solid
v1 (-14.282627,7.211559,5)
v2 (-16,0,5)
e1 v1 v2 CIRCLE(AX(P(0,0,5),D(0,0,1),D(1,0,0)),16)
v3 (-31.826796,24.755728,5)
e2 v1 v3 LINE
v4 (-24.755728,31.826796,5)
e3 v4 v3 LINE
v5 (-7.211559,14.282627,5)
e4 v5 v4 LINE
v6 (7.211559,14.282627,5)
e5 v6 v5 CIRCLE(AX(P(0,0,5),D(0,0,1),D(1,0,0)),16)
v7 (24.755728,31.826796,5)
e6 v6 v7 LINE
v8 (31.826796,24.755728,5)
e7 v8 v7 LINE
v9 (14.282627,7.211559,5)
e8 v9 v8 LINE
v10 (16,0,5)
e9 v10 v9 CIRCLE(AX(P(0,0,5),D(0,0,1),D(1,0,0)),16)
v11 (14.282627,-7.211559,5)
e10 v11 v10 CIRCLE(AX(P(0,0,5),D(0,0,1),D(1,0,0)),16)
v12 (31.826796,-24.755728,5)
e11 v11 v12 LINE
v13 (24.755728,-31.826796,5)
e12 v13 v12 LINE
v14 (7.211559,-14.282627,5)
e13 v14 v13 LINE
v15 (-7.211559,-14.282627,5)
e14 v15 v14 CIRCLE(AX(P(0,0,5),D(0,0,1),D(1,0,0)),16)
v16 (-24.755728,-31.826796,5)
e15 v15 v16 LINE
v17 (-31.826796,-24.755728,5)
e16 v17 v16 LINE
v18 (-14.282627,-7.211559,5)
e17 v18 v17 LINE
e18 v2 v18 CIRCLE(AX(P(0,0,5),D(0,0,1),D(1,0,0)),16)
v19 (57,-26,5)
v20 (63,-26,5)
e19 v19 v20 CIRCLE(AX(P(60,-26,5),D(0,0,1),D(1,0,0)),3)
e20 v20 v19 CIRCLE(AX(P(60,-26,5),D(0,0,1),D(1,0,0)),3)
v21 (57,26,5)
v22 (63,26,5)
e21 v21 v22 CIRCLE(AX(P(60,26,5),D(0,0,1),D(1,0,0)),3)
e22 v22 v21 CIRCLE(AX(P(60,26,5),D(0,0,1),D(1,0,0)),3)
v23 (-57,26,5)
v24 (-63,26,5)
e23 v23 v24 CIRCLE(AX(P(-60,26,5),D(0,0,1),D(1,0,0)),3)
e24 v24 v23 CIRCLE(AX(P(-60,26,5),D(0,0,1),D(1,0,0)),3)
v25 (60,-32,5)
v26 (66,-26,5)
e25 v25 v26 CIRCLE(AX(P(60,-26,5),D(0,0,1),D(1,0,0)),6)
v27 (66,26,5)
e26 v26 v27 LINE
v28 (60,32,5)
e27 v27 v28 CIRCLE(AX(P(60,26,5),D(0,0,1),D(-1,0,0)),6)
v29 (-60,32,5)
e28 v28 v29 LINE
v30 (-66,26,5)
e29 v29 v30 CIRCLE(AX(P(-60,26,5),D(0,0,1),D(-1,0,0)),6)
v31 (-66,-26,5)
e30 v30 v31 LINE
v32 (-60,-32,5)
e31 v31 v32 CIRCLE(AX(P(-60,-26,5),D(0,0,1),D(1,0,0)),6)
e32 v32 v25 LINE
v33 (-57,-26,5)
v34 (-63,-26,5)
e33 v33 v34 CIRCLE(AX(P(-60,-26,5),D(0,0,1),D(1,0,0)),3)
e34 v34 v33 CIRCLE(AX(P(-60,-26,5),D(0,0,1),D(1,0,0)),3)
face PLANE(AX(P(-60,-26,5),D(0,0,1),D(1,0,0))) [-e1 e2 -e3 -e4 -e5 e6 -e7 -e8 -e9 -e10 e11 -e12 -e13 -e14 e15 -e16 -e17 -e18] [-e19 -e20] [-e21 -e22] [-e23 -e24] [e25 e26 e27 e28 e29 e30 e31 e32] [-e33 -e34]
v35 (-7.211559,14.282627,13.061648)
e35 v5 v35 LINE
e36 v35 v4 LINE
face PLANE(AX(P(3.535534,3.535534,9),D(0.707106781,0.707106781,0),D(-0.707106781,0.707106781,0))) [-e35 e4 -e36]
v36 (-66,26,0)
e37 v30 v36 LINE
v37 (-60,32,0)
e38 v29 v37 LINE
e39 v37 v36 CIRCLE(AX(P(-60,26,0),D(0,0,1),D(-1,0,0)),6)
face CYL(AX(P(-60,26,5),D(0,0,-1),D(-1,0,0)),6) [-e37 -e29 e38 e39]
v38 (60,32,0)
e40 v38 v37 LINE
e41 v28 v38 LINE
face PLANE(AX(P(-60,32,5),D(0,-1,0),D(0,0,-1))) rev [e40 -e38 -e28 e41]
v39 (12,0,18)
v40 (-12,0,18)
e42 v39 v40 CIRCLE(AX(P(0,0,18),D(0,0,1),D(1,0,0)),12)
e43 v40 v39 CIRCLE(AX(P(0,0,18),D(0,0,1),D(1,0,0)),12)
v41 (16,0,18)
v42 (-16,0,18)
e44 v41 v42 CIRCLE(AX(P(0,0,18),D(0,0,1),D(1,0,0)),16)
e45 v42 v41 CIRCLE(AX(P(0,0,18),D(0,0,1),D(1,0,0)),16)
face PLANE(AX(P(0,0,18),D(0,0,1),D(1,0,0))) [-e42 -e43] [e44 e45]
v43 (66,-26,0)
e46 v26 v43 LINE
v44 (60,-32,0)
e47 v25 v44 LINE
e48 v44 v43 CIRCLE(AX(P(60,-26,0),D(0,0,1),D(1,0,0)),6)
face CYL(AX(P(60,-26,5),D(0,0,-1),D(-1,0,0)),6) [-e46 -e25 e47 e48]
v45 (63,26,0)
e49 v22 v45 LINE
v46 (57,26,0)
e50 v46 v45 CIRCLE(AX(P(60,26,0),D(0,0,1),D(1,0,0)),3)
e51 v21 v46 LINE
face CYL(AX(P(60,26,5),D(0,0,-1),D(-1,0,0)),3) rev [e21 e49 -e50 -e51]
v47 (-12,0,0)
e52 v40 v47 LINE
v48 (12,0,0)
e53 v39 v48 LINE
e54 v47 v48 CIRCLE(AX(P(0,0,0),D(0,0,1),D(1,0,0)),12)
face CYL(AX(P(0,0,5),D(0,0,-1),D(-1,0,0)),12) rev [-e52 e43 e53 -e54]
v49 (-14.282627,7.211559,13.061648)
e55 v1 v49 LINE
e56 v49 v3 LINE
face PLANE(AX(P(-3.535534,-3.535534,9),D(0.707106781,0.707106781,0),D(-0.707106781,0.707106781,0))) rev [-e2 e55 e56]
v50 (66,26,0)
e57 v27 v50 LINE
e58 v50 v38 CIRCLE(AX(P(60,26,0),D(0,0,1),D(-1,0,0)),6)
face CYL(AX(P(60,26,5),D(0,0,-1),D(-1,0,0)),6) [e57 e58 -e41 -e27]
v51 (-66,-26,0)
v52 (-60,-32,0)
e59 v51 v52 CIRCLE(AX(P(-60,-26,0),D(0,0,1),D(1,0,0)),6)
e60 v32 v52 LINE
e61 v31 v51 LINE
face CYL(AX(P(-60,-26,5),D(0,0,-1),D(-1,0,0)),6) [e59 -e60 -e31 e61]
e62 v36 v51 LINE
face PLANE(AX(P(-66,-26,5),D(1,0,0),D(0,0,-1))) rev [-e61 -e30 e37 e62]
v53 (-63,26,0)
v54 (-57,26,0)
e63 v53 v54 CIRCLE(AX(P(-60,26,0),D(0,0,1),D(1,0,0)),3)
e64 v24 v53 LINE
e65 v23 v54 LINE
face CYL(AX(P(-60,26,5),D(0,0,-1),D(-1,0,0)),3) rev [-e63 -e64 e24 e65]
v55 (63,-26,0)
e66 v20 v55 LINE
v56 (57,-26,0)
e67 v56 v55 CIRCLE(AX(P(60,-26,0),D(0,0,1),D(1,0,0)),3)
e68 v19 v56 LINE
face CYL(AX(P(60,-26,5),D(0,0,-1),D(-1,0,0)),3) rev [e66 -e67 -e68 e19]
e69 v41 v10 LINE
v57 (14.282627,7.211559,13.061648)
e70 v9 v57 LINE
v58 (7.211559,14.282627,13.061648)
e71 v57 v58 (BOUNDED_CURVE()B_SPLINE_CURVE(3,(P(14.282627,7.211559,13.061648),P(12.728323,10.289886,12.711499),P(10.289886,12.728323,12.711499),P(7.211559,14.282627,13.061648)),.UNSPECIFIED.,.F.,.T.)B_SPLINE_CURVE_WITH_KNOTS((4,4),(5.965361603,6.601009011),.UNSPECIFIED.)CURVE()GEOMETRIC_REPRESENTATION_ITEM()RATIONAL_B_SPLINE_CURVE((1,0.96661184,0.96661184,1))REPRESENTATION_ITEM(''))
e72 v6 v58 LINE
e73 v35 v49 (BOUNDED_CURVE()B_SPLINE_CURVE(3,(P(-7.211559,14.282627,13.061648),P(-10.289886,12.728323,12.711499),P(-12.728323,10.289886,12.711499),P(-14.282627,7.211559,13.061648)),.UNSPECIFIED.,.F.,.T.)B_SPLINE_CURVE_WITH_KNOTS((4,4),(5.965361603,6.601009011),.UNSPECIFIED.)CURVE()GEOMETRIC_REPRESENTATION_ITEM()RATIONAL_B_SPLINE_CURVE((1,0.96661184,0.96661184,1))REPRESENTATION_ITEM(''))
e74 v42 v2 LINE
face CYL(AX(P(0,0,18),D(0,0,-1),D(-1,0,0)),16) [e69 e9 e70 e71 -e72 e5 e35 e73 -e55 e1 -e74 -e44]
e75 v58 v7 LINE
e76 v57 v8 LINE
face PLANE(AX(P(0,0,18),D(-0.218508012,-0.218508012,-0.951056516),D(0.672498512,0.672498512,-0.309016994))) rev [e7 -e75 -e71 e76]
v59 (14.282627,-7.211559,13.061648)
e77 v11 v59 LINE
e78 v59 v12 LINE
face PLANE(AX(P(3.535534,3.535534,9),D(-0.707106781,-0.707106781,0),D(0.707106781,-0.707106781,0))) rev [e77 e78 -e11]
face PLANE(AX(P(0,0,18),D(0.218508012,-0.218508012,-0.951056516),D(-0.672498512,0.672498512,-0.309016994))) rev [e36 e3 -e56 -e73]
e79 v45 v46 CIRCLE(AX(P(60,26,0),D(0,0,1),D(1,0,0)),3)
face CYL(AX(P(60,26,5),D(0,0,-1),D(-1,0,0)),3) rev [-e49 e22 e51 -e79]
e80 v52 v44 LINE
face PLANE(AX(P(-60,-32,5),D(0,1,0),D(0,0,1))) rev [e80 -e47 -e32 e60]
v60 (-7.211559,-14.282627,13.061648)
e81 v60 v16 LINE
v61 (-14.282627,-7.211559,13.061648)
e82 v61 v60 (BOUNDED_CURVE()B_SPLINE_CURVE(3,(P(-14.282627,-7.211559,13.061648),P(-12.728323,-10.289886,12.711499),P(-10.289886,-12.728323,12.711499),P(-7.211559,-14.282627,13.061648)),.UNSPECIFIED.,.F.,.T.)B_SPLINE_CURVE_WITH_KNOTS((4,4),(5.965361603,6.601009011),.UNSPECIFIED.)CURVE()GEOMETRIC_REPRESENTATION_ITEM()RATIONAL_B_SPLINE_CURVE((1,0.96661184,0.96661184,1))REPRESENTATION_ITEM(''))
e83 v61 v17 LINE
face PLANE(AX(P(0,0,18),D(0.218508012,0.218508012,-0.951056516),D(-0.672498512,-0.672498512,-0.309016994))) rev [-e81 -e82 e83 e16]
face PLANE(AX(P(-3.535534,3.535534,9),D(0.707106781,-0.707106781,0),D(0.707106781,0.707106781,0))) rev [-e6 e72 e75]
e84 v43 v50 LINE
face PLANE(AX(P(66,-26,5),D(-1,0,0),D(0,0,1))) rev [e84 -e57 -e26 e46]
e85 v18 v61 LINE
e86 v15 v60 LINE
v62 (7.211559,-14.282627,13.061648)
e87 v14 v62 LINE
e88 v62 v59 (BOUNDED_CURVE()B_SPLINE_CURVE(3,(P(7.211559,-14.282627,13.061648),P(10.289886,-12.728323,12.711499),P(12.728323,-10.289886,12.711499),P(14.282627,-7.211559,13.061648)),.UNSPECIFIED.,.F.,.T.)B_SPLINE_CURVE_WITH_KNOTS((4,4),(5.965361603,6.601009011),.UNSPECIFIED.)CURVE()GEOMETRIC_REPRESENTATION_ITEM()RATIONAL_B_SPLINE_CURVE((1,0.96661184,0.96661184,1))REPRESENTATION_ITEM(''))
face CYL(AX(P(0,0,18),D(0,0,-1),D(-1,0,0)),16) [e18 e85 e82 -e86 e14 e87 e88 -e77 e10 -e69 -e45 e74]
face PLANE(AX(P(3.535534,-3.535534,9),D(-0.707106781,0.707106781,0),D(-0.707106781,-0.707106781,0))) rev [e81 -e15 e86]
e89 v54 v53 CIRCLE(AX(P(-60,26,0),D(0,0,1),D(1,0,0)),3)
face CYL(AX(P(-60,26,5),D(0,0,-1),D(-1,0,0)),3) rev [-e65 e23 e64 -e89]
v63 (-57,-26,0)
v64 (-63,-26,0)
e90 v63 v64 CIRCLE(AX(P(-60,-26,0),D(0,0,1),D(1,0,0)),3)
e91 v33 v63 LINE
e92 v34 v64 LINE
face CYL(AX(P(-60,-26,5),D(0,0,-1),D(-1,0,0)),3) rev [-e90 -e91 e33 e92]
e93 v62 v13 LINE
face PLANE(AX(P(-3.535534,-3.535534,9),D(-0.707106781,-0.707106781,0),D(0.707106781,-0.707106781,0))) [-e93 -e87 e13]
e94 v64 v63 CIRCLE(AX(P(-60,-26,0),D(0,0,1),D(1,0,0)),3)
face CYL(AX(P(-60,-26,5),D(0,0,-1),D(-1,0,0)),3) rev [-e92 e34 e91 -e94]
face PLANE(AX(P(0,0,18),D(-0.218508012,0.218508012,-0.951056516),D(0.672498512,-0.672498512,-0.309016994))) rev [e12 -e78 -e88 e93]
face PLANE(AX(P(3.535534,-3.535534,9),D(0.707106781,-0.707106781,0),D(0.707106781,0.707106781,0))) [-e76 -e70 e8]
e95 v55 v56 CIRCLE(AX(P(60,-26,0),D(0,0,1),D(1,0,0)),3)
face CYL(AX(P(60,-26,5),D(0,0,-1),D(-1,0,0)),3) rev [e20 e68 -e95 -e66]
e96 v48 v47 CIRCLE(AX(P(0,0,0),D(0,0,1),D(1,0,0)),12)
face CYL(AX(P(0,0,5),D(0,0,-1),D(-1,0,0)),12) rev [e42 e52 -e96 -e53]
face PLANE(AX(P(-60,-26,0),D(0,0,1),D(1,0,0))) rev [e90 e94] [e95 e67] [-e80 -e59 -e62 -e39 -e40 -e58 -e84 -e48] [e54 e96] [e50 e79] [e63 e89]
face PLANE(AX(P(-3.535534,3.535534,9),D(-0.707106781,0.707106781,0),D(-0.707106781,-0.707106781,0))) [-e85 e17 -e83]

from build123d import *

# Parameters (mm, degrees)
PLATE_PROFILE_R           = 3
PLATE_PROFILE_R_2         = 12
BASE_PLATE_132X64X5_DEPTH = 5
HUB_PROFILE_R             = 16
HUB_PROFILE_R_2           = 12
HUB_BOSS_DEPTH            = 13
HUB_RIB_10MM_REACH        = 77.525
RIB_PROFILE_WALL_W        = 198.049660708
RIB_PROFILE_WALL_H        = 10
RIB_PATTERN_4X_COUNT      = 4


with BuildPart() as part:
    # Plate Profile → Base Plate 132x64x5 (new body)
    with BuildSketch(Plane.XY):
        with BuildLine():
            Line((-60, -32), (60, -32))
            ThreePointArc((60, -32), (64.242640687, -30.242640687), (66, -26))
            Line((66, -26), (66, 26))
            ThreePointArc((66, 26), (64.242640687, 30.242640687), (60, 32))
            Line((60, 32), (-60, 32))
            ThreePointArc((-60, 32), (-64.242640687, 30.242640687), (-66, 26))
            Line((-66, 26), (-66, -26))
            ThreePointArc((-66, -26), (-64.242640687, -30.242640687), (-60, -32))
        make_face()
        with Locations((-60, 26)):
            Circle(PLATE_PROFILE_R, mode=Mode.SUBTRACT)
        with Locations((60, 26)):
            Circle(PLATE_PROFILE_R, mode=Mode.SUBTRACT)
        with Locations((60, -26)):
            Circle(PLATE_PROFILE_R, mode=Mode.SUBTRACT)
        with Locations((-60, -26)):
            Circle(PLATE_PROFILE_R, mode=Mode.SUBTRACT)
        Circle(PLATE_PROFILE_R_2, mode=Mode.SUBTRACT)
    extrude(amount=BASE_PLATE_132X64X5_DEPTH)

    # Hub Profile → Hub Boss (add)
    with BuildSketch(Plane.XY.offset(5)):
        with Locations(Location((0, 0, 0), (0, 0, 180))):
            Circle(HUB_PROFILE_R)
        Circle(HUB_PROFILE_R_2, mode=Mode.SUBTRACT)
    extrude(amount=HUB_BOSS_DEPTH)

    # Rib Profile wall → Hub Rib 10mm (add, up to next)
    with BuildSketch(Plane(origin=(-15.131216519, -15.131216519, 11.047117627), x_dir=(-0.672498511963, -0.672498511963, -0.309016994381), z_dir=(-0.218508012229, -0.218508012229, 0.951056516293)), mode=Mode.PRIVATE) as hub_rib_10mm_sk1:
        Rectangle(RIB_PROFILE_WALL_W, RIB_PROFILE_WALL_H)
    hub_rib_10mm_tool1 = extrude(hub_rib_10mm_sk1.sketch, amount=-HUB_RIB_10MM_REACH, mode=Mode.PRIVATE) - part.part
    hub_rib_10mm = hub_rib_10mm_tool1.solids().sort_by_distance((-15.131216519, -15.131216519, 11.047117627))[0]
    add(hub_rib_10mm)

    # Rib Pattern 4x: Hub Rib 10mm ×4 about axis
    rib_pattern_4x_axis = Axis((0, 0, 0), (0, 0, 1))
    for i in range(1, RIB_PATTERN_4X_COUNT):
        add(hub_rib_10mm.rotate(rib_pattern_4x_axis, i * 360 / RIB_PATTERN_4X_COUNT))


solid = part.part
